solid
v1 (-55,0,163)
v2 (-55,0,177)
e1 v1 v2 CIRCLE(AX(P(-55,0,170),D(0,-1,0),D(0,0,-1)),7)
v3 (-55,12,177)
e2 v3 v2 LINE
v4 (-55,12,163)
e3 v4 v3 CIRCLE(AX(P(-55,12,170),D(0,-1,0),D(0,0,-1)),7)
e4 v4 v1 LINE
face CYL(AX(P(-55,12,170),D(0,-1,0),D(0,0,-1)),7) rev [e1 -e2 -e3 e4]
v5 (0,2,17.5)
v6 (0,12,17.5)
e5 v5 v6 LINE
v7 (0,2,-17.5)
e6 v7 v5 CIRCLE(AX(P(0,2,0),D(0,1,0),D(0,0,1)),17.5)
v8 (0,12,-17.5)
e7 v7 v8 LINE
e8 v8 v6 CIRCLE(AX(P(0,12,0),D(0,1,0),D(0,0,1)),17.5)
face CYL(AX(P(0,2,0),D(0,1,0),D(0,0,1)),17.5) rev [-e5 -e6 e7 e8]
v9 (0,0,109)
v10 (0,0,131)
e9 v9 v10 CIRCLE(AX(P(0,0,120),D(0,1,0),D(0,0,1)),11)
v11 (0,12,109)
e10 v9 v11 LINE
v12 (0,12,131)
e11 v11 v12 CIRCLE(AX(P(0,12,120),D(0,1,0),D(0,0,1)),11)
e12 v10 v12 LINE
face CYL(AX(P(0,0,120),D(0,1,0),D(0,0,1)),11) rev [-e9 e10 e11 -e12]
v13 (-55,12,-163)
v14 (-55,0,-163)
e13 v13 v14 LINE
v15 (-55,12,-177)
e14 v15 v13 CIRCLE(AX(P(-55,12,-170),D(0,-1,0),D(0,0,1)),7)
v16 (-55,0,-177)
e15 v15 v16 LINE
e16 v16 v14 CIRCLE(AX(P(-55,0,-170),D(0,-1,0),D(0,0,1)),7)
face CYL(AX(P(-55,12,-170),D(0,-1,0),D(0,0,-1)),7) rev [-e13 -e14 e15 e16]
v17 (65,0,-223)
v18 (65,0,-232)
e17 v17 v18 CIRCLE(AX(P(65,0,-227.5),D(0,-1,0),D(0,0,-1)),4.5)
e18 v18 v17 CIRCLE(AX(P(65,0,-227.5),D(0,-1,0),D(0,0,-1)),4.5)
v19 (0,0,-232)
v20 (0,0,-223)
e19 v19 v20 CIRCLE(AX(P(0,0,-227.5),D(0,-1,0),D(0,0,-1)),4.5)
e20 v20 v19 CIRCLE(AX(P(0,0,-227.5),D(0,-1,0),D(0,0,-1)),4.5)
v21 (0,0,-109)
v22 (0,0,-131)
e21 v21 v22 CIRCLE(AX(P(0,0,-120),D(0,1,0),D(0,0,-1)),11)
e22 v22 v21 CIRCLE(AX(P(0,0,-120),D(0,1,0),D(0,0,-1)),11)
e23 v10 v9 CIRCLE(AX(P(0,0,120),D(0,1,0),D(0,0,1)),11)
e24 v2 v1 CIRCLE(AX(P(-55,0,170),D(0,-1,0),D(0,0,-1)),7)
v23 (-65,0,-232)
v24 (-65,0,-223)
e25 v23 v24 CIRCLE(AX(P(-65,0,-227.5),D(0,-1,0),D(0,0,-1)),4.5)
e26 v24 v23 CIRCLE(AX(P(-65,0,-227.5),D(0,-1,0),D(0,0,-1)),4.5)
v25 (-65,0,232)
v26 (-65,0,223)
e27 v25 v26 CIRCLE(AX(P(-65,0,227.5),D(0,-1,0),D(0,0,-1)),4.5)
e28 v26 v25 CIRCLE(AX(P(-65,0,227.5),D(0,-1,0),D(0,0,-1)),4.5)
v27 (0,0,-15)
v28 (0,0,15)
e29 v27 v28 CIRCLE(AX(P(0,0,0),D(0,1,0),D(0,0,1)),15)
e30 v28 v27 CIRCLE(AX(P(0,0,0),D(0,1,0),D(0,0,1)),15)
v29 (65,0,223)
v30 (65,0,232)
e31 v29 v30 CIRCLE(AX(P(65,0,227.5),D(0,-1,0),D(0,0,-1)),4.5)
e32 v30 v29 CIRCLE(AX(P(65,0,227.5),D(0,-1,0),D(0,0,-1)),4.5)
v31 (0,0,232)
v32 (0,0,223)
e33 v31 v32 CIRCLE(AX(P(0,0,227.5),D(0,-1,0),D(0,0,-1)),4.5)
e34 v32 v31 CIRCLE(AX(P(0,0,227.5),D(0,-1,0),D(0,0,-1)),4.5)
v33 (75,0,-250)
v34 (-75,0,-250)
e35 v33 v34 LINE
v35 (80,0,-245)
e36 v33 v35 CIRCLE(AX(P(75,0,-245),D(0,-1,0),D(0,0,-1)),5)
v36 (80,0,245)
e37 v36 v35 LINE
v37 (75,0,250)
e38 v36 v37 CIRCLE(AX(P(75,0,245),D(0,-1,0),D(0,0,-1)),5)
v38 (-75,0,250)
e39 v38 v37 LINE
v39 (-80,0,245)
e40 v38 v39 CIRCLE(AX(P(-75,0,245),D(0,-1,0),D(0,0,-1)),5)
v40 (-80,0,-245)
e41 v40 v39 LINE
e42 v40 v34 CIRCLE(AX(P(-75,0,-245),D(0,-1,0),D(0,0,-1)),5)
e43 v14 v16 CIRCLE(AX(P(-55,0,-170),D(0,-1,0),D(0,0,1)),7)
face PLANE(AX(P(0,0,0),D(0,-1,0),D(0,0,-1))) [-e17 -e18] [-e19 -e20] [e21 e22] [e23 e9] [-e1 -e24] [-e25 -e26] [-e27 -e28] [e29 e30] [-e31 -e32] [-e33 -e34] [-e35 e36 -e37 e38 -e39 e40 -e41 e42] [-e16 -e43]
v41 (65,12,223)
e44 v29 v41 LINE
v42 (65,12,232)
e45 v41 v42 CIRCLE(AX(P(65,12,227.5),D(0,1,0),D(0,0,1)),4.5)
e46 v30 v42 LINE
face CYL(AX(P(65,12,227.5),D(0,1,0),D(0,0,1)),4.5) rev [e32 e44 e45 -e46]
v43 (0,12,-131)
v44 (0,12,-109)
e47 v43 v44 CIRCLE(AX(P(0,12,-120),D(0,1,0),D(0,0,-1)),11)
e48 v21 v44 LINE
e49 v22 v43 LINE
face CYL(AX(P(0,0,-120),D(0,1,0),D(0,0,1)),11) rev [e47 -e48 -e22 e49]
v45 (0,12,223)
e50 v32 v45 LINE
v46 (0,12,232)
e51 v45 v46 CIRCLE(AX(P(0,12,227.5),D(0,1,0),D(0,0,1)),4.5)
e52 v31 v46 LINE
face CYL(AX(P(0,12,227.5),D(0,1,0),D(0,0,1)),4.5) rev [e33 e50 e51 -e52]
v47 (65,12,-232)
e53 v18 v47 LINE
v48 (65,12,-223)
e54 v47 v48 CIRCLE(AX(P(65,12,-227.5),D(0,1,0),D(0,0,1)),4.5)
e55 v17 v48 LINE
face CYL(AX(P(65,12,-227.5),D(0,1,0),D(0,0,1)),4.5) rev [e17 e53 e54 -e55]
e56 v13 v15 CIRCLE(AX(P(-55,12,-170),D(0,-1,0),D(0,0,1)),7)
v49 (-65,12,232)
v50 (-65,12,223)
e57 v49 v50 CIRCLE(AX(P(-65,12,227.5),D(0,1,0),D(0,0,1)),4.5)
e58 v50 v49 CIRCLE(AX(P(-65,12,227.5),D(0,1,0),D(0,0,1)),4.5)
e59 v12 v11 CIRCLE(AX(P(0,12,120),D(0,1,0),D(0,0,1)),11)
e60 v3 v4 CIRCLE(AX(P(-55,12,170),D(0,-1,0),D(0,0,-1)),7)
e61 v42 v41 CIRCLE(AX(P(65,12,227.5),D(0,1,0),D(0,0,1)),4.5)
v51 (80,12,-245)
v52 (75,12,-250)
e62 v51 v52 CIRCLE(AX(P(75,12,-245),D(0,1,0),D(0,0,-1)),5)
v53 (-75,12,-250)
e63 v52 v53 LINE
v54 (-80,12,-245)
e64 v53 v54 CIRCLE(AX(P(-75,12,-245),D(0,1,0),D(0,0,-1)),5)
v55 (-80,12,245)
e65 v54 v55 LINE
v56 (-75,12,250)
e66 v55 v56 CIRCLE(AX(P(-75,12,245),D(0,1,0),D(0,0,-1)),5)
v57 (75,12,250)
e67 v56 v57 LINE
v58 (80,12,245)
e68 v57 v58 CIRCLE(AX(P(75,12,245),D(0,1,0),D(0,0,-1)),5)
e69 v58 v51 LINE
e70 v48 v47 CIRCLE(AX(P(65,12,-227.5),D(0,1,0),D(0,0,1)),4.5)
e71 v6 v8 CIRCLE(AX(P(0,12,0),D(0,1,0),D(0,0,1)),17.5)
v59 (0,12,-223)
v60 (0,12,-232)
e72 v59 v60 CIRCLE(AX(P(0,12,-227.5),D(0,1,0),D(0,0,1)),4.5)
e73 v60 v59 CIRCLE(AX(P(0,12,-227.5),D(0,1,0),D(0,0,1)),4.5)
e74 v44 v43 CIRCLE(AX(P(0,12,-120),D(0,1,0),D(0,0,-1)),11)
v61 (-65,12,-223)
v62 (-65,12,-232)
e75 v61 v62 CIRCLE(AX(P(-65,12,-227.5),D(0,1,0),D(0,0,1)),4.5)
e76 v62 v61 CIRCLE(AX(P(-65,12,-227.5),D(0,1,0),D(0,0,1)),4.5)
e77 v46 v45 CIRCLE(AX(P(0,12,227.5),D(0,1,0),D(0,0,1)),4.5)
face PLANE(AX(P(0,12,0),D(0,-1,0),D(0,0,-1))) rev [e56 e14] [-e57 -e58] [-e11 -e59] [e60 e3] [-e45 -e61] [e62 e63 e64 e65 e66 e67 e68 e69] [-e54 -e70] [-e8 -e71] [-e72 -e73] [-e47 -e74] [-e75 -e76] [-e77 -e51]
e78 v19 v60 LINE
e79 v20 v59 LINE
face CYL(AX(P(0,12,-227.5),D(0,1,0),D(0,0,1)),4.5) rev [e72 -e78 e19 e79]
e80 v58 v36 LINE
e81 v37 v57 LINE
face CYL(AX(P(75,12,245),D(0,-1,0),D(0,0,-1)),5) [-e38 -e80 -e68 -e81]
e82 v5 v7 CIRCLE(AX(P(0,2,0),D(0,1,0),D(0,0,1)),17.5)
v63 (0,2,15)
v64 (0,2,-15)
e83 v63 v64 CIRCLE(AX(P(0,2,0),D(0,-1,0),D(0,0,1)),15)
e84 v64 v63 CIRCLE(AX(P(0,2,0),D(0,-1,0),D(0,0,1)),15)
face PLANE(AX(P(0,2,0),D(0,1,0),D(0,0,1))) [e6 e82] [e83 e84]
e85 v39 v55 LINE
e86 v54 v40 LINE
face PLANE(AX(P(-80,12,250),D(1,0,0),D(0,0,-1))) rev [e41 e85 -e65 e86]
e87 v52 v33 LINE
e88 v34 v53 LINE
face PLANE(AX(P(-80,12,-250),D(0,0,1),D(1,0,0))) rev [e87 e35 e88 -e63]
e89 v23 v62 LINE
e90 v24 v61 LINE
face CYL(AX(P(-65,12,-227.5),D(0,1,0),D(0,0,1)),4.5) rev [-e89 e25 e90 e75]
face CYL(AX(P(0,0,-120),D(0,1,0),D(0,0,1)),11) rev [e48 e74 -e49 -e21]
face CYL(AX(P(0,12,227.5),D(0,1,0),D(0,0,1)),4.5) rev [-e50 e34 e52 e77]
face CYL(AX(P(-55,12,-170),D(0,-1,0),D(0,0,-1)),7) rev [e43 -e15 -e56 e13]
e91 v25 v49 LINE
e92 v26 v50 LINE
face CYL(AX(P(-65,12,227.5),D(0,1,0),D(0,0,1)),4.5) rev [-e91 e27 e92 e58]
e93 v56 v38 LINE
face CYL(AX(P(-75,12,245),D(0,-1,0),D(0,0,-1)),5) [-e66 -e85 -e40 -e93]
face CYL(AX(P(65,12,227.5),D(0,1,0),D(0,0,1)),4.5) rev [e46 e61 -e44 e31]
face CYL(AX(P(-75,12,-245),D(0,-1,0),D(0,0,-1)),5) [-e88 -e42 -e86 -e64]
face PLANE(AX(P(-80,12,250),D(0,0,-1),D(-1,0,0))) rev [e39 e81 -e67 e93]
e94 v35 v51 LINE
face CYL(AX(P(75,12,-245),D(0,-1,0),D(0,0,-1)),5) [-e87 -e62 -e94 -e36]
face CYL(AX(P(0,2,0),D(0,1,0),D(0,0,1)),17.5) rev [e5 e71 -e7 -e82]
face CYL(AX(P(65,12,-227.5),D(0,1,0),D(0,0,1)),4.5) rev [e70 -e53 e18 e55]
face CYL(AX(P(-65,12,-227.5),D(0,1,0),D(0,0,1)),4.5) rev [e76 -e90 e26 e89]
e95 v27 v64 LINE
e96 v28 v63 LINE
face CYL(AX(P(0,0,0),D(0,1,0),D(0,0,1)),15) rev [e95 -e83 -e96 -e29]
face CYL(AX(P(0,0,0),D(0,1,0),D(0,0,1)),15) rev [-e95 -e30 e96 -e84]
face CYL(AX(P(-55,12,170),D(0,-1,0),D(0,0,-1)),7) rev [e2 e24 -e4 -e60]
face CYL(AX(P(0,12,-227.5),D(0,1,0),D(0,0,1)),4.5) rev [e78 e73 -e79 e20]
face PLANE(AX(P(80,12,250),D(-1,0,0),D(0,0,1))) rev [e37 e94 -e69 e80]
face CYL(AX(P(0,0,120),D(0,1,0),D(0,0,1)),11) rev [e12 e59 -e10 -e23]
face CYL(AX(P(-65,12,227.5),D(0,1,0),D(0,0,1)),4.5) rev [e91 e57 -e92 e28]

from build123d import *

# Parameters (mm, degrees)
SKETCH1_W                    = 160
SKETCH1_H                    = 500
BOSS_EXTRUDE1_DEPTH          = 12
SKETCH2_R                    = 15
SKETCH2_R_2                  = 11
CUT_EXTRUDE1_DEPTH           = 12
SKETCH3_R                    = 17.5
CUT_EXTRUDE2_DEPTH           = 10
F_9_0_9_DIAMETER_HOLE1_D     = 9
F_9_0_9_DIAMETER_HOLE1_DEPTH = 13
F_9_0_9_DIAMETER_HOLE1_TIP   = 2.703872786
FILLET1_R                    = 5
SKETCH7_R                    = 7
CUT_EXTRUDE3_DEPTH           = 263.762249952


with BuildPart() as part:
    # Sketch1 → Boss-Extrude1 (new body)
    with BuildSketch(Plane(origin=(0, 0, 0), x_dir=(1, 0, 0), z_dir=(0, 1, 0))):
        Rectangle(SKETCH1_W, SKETCH1_H)
    extrude(amount=BOSS_EXTRUDE1_DEPTH)

    # Sketch2 → Cut-Extrude1 (cut)
    with BuildSketch(Plane(origin=(0, 12, 0), x_dir=(1, 0, 0), z_dir=(0, 1, 0))):
        with Locations(Location((0, 0, 0), (0, 0, 270))):
            Circle(SKETCH2_R)
        with Locations(Location((0, -120, 0), (0, 0, 270))):
            Circle(SKETCH2_R_2)
        with Locations(Location((0, 120, 0), (0, 0, 90))):
            Circle(SKETCH2_R_2)
    extrude(amount=-CUT_EXTRUDE1_DEPTH, mode=Mode.SUBTRACT)

    # Sketch3 → Cut-Extrude2 (cut)
    with BuildSketch(Plane(origin=(0, 12, 0), x_dir=(1, 0, 0), z_dir=(0, 1, 0))):
        with Locations(Location((0, 0, 0), (0, 0, 270))):
            Circle(SKETCH3_R)
    extrude(amount=-CUT_EXTRUDE2_DEPTH, mode=Mode.SUBTRACT)

    # Ø9.0 (9) Diameter Hole1
    with Locations(Plane(origin=(0, 12, 0), x_dir=(1, 0, 0), z_dir=(0, 1, 0))):
        with Locations((-65, 227.5), (0, 227.5), (65, 227.5), (-65, -227.5), (0, -227.5), (65, -227.5)):
            Hole(F_9_0_9_DIAMETER_HOLE1_D / 2, depth=F_9_0_9_DIAMETER_HOLE1_DEPTH)
            with Locations((0, 0, -(F_9_0_9_DIAMETER_HOLE1_DEPTH + F_9_0_9_DIAMETER_HOLE1_TIP / 2))):  # 118° drill point
                Cone(0, F_9_0_9_DIAMETER_HOLE1_D / 2, F_9_0_9_DIAMETER_HOLE1_TIP, mode=Mode.SUBTRACT)

    # Fillet1
    fillet1_edges = [part.edges().sort_by_distance(p)[0] for p in [
        (80, 6, 250),
        (-80, 6, 250),
        (-80, 6, -250),
        (80, 6, -250),
    ]]
    fillet(fillet1_edges, radius=FILLET1_R)

    # Sketch7 → Cut-Extrude3 (cut, through all)
    with BuildSketch(Plane.XZ):
        with Locations(Location((-55, 170, 0), (0, 0, 270))):
            Circle(SKETCH7_R)
        with Locations(Location((-55, -170, 0), (0, 0, 90))):
            Circle(SKETCH7_R)
    extrude(amount=-CUT_EXTRUDE3_DEPTH, mode=Mode.SUBTRACT)


solid = part.part
